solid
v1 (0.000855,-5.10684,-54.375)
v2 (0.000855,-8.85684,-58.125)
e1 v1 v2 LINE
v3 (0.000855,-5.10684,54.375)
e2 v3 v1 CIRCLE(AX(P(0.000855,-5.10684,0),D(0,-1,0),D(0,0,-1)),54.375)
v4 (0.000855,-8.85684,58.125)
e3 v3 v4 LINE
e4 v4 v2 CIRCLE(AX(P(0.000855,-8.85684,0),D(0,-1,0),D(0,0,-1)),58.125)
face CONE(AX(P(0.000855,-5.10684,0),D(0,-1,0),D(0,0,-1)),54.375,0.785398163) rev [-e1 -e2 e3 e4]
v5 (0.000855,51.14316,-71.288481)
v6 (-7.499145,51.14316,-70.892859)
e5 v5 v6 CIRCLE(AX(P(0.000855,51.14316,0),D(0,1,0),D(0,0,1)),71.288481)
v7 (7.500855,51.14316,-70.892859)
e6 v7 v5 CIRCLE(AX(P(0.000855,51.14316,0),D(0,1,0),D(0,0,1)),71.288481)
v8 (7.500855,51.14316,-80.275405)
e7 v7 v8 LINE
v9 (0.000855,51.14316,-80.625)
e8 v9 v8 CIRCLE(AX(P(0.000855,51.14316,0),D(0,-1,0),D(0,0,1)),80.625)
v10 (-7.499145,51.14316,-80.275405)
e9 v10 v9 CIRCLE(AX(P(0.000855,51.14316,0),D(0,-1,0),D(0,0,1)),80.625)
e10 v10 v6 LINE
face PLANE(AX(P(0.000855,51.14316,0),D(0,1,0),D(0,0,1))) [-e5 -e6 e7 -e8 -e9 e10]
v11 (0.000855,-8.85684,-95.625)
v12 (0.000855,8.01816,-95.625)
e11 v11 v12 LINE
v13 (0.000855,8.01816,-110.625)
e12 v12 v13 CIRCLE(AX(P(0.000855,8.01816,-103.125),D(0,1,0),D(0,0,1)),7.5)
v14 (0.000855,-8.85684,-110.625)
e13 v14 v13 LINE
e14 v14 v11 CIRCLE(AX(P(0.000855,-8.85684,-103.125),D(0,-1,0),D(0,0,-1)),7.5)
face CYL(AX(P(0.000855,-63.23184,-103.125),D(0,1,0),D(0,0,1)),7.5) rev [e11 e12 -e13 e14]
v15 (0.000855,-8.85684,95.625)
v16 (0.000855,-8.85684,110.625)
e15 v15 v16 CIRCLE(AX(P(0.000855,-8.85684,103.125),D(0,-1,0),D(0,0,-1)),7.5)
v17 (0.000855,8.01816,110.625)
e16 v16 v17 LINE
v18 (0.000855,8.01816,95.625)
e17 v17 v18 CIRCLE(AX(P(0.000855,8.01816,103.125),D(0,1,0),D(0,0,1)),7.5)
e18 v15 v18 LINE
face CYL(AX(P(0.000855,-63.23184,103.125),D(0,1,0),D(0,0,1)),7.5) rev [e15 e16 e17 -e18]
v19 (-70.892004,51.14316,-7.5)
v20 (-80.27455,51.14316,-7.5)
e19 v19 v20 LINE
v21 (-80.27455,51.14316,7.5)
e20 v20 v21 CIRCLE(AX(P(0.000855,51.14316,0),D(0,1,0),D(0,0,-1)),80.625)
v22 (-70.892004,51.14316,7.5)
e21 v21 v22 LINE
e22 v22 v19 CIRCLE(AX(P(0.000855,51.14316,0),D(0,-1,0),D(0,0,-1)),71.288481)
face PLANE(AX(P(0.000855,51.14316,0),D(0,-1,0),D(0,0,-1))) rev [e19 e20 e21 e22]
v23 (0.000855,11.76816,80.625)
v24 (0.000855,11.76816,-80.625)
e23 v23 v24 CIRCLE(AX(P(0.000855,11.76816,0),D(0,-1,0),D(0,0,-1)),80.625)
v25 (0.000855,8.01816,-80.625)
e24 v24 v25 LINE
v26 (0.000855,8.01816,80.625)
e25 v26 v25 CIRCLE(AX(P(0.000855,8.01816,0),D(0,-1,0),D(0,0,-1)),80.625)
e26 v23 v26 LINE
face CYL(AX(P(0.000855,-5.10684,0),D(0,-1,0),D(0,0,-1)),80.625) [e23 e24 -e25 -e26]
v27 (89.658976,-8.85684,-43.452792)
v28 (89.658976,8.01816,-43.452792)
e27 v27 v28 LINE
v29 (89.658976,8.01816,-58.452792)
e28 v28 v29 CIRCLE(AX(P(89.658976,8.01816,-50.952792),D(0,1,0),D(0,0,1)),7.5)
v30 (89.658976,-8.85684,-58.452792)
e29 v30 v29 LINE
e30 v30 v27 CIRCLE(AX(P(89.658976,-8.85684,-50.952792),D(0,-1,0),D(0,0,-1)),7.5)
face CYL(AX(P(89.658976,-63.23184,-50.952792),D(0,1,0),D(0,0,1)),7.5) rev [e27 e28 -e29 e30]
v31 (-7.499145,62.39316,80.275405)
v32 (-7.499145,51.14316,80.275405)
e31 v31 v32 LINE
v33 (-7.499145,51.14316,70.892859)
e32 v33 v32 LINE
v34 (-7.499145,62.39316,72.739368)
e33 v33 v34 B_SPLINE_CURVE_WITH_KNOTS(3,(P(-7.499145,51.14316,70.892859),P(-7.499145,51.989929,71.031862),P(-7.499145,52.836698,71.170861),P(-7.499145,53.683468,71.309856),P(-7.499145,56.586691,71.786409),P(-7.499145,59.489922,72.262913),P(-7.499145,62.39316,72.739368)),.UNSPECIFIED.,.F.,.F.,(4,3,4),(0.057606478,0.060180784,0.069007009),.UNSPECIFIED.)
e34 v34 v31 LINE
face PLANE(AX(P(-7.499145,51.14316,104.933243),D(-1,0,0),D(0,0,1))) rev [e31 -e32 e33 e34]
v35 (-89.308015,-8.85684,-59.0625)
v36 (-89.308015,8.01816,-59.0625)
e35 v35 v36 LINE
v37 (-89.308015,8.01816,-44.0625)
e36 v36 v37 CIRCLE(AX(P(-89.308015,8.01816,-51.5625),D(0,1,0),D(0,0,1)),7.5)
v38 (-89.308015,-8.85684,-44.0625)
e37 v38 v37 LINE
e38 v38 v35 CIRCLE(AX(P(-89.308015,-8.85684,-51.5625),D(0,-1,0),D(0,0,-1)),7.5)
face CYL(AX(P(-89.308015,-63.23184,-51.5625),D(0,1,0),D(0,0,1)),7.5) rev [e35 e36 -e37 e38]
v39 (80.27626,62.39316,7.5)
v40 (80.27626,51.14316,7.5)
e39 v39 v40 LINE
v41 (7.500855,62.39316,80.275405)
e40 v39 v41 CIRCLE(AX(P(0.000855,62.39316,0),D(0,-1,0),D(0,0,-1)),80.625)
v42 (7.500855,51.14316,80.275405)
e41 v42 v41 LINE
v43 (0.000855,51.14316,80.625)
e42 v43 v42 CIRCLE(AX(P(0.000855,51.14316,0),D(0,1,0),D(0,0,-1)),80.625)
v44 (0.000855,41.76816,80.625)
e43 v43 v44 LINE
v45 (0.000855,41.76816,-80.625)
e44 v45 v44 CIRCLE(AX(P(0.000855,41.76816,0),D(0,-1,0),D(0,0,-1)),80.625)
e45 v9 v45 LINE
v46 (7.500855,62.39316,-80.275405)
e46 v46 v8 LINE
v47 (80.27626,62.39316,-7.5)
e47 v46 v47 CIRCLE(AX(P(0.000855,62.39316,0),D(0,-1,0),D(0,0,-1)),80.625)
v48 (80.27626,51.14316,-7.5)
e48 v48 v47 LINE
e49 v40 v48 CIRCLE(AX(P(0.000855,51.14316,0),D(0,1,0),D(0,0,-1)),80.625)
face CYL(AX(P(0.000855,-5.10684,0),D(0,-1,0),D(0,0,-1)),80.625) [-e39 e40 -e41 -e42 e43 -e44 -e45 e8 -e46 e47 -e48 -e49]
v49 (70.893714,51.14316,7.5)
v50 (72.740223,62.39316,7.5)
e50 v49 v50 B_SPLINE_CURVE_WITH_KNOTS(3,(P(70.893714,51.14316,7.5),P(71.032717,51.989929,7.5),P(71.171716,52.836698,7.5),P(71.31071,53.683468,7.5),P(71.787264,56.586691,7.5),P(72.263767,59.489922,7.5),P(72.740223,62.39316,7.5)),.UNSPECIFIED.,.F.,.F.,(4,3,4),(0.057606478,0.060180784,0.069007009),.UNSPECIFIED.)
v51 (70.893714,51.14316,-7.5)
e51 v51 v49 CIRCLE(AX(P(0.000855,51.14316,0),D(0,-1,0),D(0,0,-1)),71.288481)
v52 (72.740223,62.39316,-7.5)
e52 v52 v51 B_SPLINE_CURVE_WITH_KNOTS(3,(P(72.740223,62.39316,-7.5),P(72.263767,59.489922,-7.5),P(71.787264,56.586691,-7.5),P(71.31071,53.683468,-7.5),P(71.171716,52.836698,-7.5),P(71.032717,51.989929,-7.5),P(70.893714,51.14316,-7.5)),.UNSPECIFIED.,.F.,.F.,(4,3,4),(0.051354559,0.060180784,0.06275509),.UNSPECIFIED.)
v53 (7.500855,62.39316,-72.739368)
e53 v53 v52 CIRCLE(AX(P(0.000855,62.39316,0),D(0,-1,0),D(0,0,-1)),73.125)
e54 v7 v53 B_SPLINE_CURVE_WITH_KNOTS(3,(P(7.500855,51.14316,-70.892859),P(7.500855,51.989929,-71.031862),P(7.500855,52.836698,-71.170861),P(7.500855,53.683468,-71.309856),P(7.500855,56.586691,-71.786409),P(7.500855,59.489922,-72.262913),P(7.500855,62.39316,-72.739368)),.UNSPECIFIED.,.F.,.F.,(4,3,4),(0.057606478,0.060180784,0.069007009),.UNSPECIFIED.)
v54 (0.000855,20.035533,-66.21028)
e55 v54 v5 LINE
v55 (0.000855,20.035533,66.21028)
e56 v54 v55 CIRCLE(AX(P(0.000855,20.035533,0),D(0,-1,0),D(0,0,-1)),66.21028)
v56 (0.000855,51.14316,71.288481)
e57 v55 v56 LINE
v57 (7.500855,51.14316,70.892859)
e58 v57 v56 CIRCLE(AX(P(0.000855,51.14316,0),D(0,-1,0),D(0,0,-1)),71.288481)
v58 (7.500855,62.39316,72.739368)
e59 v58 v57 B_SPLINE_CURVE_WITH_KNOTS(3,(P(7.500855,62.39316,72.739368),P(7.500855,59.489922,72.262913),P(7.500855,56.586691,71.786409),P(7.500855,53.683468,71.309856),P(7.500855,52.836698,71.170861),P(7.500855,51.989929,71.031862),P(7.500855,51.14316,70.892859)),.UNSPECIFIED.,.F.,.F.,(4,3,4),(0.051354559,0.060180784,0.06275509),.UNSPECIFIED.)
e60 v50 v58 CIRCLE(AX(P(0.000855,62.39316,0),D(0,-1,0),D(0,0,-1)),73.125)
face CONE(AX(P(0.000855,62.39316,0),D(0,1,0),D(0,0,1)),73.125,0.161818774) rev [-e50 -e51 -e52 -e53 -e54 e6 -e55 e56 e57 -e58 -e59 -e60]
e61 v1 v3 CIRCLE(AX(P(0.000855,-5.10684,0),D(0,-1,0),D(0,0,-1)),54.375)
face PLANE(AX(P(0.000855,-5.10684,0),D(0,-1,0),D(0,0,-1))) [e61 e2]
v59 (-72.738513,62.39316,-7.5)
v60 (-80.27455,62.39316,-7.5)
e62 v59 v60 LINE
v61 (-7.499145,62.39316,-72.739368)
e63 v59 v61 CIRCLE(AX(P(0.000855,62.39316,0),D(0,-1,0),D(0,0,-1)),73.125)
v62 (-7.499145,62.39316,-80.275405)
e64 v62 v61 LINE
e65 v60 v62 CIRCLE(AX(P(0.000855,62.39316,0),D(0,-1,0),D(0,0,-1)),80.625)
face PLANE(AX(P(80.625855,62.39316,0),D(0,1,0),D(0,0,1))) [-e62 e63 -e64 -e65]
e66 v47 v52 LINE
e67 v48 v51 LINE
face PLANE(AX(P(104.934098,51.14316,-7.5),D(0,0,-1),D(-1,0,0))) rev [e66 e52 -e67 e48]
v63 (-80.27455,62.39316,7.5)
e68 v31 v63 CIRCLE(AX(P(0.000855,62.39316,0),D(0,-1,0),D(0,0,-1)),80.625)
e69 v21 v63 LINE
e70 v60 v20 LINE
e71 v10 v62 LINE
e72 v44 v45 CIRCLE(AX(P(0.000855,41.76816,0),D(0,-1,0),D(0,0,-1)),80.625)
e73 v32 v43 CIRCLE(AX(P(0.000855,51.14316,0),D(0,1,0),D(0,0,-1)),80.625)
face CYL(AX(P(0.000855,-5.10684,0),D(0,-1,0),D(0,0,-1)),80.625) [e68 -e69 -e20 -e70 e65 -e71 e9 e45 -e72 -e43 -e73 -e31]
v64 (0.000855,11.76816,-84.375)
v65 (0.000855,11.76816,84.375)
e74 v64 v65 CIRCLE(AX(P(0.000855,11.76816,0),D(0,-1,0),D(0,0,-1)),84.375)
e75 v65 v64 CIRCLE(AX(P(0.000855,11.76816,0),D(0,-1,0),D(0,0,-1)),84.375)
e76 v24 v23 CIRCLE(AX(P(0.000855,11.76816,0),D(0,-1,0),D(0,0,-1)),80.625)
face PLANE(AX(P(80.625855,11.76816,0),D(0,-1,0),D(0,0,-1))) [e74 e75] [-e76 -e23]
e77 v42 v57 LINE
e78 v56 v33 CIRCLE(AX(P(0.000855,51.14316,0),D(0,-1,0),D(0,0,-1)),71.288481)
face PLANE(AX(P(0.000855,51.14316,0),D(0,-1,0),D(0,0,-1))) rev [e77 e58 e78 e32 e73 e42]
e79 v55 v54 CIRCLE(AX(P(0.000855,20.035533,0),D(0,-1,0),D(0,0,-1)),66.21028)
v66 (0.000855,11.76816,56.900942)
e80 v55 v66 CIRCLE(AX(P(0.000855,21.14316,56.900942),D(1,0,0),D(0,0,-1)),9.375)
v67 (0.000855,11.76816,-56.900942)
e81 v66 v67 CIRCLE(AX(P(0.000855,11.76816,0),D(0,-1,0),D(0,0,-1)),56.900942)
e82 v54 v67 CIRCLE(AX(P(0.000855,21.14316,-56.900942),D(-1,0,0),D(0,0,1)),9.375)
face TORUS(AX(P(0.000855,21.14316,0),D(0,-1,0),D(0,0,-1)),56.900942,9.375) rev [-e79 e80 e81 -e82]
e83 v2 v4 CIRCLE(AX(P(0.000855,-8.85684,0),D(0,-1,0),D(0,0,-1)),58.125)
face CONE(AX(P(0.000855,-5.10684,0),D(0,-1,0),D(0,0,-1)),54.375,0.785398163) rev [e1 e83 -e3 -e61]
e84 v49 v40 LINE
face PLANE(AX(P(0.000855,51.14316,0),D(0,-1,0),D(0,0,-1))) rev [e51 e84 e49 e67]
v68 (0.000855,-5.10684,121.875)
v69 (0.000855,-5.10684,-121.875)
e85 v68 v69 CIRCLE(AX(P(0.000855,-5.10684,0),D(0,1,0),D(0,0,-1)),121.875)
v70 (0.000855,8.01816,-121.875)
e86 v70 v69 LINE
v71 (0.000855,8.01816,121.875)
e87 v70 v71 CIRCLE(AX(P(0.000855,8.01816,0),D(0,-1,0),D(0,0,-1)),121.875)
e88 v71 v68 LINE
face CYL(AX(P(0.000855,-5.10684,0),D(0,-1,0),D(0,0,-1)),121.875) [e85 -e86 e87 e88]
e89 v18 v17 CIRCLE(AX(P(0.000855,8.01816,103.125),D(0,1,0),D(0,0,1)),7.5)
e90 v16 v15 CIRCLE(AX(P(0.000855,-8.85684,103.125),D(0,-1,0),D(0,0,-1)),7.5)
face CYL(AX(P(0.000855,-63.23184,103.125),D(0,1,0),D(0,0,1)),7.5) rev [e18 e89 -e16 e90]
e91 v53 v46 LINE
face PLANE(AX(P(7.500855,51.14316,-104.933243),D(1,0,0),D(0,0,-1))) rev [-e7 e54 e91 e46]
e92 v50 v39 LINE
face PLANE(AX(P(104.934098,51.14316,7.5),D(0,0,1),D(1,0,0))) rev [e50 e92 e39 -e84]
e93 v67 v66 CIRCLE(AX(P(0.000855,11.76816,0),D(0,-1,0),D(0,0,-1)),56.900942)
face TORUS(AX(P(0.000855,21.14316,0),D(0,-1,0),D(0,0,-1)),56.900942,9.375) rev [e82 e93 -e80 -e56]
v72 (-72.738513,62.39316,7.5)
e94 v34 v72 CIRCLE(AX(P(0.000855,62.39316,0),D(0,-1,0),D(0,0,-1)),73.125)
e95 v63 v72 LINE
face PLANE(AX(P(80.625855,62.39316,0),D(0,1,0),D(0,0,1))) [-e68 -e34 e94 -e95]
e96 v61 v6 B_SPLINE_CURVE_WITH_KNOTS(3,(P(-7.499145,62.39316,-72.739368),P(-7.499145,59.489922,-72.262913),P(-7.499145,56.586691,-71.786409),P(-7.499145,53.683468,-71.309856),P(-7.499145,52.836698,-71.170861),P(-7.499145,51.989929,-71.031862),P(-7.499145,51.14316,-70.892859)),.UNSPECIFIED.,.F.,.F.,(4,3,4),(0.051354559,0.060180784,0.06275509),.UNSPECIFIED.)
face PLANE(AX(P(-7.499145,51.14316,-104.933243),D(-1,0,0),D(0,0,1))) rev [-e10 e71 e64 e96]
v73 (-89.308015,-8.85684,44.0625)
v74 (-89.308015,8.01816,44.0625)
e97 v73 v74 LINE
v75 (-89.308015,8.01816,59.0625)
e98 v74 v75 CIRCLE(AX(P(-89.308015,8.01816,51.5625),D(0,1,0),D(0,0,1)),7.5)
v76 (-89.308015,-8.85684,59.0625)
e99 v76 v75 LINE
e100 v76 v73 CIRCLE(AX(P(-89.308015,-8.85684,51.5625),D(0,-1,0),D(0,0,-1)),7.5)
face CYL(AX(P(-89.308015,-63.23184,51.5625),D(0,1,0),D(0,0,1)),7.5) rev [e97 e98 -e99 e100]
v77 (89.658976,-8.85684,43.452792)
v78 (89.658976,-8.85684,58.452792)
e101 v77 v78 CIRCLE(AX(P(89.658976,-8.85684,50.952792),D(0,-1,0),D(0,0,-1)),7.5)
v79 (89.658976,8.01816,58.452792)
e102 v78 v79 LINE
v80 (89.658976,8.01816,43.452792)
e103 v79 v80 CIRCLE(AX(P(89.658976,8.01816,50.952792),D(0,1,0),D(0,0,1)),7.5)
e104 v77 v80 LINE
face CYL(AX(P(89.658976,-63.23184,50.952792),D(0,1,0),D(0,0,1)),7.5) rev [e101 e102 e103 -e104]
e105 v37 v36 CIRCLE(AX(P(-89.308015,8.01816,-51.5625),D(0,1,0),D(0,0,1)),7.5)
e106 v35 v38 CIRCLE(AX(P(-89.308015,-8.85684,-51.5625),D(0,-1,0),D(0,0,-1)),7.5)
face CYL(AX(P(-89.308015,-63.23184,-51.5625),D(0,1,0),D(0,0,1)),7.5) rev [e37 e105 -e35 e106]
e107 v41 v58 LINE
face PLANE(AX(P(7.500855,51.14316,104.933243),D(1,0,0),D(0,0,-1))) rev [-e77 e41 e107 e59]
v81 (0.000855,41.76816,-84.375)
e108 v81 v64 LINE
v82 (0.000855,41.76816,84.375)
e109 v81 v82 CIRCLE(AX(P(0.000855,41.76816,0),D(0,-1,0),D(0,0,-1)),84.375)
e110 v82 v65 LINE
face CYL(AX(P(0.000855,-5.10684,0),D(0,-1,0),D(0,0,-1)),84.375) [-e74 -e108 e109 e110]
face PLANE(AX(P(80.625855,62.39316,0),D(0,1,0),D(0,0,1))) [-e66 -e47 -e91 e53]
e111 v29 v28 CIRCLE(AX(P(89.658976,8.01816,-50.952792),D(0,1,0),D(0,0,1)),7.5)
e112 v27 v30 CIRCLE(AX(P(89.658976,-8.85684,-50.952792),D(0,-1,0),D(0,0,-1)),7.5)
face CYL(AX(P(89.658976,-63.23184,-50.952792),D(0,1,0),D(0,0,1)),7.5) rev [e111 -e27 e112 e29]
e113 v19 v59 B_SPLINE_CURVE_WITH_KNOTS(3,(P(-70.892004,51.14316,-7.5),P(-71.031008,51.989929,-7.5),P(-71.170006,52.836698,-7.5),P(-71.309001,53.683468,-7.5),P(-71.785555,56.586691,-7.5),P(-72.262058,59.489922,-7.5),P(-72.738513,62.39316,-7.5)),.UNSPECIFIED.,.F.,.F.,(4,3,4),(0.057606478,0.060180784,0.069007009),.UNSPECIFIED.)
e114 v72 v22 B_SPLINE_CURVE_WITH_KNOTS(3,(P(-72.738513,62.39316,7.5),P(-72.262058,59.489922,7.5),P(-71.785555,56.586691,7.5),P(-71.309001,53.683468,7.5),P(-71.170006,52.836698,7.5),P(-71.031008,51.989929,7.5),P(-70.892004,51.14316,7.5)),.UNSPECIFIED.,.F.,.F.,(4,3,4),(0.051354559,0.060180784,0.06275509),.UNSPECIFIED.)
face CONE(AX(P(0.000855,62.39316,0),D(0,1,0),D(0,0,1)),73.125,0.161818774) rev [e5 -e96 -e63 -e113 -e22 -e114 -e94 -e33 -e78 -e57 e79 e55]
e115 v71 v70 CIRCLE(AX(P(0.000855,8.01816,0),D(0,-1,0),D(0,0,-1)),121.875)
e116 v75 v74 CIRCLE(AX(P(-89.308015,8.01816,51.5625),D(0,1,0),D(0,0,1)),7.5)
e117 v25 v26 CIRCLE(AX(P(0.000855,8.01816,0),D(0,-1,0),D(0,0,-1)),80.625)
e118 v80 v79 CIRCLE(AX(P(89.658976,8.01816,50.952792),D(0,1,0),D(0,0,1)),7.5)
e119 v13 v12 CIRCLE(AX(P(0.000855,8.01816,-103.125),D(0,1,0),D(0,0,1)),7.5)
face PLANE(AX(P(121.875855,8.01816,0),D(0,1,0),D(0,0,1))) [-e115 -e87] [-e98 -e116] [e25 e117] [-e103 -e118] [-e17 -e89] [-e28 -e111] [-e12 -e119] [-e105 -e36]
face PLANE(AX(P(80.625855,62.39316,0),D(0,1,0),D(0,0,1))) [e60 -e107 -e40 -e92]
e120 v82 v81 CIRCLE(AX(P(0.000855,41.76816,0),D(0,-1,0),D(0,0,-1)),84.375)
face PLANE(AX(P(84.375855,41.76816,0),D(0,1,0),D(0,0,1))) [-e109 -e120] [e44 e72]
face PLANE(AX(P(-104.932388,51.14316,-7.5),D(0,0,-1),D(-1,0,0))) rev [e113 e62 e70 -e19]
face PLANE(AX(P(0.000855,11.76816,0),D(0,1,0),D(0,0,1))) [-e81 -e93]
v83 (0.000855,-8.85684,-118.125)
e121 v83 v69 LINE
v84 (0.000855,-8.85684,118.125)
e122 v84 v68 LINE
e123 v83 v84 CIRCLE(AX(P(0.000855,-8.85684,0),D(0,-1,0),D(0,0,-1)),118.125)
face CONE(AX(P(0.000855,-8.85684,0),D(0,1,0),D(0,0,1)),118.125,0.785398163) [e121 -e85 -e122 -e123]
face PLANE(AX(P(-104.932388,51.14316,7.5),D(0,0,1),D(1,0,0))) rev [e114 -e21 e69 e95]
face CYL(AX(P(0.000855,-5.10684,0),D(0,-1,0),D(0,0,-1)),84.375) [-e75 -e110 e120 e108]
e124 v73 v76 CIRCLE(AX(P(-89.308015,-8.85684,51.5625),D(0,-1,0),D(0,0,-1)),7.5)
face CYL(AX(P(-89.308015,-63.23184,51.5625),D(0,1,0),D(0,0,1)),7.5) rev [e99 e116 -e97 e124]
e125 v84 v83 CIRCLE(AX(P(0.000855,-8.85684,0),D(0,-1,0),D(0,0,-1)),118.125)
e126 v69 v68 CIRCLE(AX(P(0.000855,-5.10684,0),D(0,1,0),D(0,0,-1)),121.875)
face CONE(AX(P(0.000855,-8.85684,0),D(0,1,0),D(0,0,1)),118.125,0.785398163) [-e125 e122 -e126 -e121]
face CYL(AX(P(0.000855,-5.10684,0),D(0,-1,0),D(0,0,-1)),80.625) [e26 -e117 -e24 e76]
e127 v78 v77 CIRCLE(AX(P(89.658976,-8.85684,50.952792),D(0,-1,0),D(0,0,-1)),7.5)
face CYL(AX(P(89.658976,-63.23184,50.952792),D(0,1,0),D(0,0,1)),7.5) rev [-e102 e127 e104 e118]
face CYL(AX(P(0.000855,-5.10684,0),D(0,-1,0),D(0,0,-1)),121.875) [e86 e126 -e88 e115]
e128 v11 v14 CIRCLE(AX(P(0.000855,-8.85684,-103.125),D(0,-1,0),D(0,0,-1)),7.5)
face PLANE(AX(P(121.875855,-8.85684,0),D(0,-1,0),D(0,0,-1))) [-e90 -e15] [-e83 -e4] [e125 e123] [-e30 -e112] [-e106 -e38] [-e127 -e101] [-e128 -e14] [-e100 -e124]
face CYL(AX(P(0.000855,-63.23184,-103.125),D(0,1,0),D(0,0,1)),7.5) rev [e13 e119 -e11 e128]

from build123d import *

# Parameters (mm, degrees)
SKETCH3_W          = 31.782249742
SKETCH3_H          = 8
SKETCH3_W_2        = 8
SKETCH3_H_2        = 31.782249742
CUT_EXTRUDE1_DEPTH = 6
CHAMFER1_SIZE      = 2
SKETCH4_R          = 4
CUT_EXTRUDE2_DEPTH = 67
SCALE_1_SCALE      = 1.875


with BuildPart() as part:
    # Sketch2 → Revolve1 (revolve)
    with BuildSketch(Plane.XY, mode=Mode.PRIVATE) as revolve1_sk:
        with BuildLine():
            Line((65, 9), (65, 0))
            Line((65, 0), (31, 0))
            Line((31, 0), (29, 2))
            Line((29, 2), (0, 2))
            Line((0, 2), (0, 11))
            Line((0, 11), (30.347168885, 11))
            ThreePointArc((30.347168885, 11), (33.667283917, 12.261439291), (35.312149528, 15.40926553))
            Line((35.312149528, 15.40926553), (39, 38))
            Line((39, 38), (43, 38))
            Line((43, 38), (43, 27))
            Line((43, 27), (45, 27))
            Line((45, 27), (45, 11))
            Line((45, 11), (43, 11))
            Line((43, 11), (43, 9))
            Line((43, 9), (65, 9))
        make_face()
    revolve(revolve1_sk.sketch.rotate(Axis((0, 2, 0), (0, 1, 0)), 90), axis=Axis((0, 2, 0), (0, 1, 0)))

    # Sketch3 → Cut-Extrude1 (cut)
    with BuildSketch(Plane(origin=(0, 38, 0), x_dir=(1, 0, 0), z_dir=(0, 1, 0))):
        with Locations((40.073271414, 0)):
            Rectangle(SKETCH3_W, SKETCH3_H)
        with Locations((0, 40.073271414)):
            Rectangle(SKETCH3_W_2, SKETCH3_H_2)
        with Locations((0, -40.073271414)):
            Rectangle(SKETCH3_W_2, SKETCH3_H_2)
        with Locations((-40.073271414, 0)):
            Rectangle(SKETCH3_W, SKETCH3_H)
    extrude(amount=-CUT_EXTRUDE1_DEPTH, mode=Mode.SUBTRACT)

    # Chamfer1
    chamfer1_edges = [part.edges().sort_by_distance(p)[0] for p in [
        (0, 0, 65),
    ]]
    chamfer(chamfer1_edges, length=CHAMFER1_SIZE)

    # Sketch4 → Cut-Extrude2 (cut)
    with BuildSketch(Plane(origin=(0, 38, 0), x_dir=(1, 0, 0), z_dir=(0, 1, 0))):
        with Locations(Location((0, 55, 0), (0, 0, 270))):
            Circle(SKETCH4_R)
        with Locations(Location((47.817664455, 27.174822282, 0), (0, 0, 270))):
            Circle(SKETCH4_R)
        with Locations(Location((-47.631397208, 27.5, 0), (0, 0, 270))):
            Circle(SKETCH4_R)
        with Locations(Location((-47.631397208, -27.5, 0), (0, 0, 270))):
            Circle(SKETCH4_R)
        with Locations(Location((0, -55, 0), (0, 0, 270))):
            Circle(SKETCH4_R)
        with Locations(Location((47.817664455, -27.174822282, 0), (0, 0, 270))):
            Circle(SKETCH4_R)
    extrude(amount=-CUT_EXTRUDE2_DEPTH, mode=Mode.SUBTRACT)


with BuildPart() as part_1:
    # Scale 1: scaled about (-0.000976977, 10.122102603, 0)
    add(part.part.scale(SCALE_1_SCALE).moved(Location((0.000854855, -8.856839778, 0))))


solid = part_1.part
